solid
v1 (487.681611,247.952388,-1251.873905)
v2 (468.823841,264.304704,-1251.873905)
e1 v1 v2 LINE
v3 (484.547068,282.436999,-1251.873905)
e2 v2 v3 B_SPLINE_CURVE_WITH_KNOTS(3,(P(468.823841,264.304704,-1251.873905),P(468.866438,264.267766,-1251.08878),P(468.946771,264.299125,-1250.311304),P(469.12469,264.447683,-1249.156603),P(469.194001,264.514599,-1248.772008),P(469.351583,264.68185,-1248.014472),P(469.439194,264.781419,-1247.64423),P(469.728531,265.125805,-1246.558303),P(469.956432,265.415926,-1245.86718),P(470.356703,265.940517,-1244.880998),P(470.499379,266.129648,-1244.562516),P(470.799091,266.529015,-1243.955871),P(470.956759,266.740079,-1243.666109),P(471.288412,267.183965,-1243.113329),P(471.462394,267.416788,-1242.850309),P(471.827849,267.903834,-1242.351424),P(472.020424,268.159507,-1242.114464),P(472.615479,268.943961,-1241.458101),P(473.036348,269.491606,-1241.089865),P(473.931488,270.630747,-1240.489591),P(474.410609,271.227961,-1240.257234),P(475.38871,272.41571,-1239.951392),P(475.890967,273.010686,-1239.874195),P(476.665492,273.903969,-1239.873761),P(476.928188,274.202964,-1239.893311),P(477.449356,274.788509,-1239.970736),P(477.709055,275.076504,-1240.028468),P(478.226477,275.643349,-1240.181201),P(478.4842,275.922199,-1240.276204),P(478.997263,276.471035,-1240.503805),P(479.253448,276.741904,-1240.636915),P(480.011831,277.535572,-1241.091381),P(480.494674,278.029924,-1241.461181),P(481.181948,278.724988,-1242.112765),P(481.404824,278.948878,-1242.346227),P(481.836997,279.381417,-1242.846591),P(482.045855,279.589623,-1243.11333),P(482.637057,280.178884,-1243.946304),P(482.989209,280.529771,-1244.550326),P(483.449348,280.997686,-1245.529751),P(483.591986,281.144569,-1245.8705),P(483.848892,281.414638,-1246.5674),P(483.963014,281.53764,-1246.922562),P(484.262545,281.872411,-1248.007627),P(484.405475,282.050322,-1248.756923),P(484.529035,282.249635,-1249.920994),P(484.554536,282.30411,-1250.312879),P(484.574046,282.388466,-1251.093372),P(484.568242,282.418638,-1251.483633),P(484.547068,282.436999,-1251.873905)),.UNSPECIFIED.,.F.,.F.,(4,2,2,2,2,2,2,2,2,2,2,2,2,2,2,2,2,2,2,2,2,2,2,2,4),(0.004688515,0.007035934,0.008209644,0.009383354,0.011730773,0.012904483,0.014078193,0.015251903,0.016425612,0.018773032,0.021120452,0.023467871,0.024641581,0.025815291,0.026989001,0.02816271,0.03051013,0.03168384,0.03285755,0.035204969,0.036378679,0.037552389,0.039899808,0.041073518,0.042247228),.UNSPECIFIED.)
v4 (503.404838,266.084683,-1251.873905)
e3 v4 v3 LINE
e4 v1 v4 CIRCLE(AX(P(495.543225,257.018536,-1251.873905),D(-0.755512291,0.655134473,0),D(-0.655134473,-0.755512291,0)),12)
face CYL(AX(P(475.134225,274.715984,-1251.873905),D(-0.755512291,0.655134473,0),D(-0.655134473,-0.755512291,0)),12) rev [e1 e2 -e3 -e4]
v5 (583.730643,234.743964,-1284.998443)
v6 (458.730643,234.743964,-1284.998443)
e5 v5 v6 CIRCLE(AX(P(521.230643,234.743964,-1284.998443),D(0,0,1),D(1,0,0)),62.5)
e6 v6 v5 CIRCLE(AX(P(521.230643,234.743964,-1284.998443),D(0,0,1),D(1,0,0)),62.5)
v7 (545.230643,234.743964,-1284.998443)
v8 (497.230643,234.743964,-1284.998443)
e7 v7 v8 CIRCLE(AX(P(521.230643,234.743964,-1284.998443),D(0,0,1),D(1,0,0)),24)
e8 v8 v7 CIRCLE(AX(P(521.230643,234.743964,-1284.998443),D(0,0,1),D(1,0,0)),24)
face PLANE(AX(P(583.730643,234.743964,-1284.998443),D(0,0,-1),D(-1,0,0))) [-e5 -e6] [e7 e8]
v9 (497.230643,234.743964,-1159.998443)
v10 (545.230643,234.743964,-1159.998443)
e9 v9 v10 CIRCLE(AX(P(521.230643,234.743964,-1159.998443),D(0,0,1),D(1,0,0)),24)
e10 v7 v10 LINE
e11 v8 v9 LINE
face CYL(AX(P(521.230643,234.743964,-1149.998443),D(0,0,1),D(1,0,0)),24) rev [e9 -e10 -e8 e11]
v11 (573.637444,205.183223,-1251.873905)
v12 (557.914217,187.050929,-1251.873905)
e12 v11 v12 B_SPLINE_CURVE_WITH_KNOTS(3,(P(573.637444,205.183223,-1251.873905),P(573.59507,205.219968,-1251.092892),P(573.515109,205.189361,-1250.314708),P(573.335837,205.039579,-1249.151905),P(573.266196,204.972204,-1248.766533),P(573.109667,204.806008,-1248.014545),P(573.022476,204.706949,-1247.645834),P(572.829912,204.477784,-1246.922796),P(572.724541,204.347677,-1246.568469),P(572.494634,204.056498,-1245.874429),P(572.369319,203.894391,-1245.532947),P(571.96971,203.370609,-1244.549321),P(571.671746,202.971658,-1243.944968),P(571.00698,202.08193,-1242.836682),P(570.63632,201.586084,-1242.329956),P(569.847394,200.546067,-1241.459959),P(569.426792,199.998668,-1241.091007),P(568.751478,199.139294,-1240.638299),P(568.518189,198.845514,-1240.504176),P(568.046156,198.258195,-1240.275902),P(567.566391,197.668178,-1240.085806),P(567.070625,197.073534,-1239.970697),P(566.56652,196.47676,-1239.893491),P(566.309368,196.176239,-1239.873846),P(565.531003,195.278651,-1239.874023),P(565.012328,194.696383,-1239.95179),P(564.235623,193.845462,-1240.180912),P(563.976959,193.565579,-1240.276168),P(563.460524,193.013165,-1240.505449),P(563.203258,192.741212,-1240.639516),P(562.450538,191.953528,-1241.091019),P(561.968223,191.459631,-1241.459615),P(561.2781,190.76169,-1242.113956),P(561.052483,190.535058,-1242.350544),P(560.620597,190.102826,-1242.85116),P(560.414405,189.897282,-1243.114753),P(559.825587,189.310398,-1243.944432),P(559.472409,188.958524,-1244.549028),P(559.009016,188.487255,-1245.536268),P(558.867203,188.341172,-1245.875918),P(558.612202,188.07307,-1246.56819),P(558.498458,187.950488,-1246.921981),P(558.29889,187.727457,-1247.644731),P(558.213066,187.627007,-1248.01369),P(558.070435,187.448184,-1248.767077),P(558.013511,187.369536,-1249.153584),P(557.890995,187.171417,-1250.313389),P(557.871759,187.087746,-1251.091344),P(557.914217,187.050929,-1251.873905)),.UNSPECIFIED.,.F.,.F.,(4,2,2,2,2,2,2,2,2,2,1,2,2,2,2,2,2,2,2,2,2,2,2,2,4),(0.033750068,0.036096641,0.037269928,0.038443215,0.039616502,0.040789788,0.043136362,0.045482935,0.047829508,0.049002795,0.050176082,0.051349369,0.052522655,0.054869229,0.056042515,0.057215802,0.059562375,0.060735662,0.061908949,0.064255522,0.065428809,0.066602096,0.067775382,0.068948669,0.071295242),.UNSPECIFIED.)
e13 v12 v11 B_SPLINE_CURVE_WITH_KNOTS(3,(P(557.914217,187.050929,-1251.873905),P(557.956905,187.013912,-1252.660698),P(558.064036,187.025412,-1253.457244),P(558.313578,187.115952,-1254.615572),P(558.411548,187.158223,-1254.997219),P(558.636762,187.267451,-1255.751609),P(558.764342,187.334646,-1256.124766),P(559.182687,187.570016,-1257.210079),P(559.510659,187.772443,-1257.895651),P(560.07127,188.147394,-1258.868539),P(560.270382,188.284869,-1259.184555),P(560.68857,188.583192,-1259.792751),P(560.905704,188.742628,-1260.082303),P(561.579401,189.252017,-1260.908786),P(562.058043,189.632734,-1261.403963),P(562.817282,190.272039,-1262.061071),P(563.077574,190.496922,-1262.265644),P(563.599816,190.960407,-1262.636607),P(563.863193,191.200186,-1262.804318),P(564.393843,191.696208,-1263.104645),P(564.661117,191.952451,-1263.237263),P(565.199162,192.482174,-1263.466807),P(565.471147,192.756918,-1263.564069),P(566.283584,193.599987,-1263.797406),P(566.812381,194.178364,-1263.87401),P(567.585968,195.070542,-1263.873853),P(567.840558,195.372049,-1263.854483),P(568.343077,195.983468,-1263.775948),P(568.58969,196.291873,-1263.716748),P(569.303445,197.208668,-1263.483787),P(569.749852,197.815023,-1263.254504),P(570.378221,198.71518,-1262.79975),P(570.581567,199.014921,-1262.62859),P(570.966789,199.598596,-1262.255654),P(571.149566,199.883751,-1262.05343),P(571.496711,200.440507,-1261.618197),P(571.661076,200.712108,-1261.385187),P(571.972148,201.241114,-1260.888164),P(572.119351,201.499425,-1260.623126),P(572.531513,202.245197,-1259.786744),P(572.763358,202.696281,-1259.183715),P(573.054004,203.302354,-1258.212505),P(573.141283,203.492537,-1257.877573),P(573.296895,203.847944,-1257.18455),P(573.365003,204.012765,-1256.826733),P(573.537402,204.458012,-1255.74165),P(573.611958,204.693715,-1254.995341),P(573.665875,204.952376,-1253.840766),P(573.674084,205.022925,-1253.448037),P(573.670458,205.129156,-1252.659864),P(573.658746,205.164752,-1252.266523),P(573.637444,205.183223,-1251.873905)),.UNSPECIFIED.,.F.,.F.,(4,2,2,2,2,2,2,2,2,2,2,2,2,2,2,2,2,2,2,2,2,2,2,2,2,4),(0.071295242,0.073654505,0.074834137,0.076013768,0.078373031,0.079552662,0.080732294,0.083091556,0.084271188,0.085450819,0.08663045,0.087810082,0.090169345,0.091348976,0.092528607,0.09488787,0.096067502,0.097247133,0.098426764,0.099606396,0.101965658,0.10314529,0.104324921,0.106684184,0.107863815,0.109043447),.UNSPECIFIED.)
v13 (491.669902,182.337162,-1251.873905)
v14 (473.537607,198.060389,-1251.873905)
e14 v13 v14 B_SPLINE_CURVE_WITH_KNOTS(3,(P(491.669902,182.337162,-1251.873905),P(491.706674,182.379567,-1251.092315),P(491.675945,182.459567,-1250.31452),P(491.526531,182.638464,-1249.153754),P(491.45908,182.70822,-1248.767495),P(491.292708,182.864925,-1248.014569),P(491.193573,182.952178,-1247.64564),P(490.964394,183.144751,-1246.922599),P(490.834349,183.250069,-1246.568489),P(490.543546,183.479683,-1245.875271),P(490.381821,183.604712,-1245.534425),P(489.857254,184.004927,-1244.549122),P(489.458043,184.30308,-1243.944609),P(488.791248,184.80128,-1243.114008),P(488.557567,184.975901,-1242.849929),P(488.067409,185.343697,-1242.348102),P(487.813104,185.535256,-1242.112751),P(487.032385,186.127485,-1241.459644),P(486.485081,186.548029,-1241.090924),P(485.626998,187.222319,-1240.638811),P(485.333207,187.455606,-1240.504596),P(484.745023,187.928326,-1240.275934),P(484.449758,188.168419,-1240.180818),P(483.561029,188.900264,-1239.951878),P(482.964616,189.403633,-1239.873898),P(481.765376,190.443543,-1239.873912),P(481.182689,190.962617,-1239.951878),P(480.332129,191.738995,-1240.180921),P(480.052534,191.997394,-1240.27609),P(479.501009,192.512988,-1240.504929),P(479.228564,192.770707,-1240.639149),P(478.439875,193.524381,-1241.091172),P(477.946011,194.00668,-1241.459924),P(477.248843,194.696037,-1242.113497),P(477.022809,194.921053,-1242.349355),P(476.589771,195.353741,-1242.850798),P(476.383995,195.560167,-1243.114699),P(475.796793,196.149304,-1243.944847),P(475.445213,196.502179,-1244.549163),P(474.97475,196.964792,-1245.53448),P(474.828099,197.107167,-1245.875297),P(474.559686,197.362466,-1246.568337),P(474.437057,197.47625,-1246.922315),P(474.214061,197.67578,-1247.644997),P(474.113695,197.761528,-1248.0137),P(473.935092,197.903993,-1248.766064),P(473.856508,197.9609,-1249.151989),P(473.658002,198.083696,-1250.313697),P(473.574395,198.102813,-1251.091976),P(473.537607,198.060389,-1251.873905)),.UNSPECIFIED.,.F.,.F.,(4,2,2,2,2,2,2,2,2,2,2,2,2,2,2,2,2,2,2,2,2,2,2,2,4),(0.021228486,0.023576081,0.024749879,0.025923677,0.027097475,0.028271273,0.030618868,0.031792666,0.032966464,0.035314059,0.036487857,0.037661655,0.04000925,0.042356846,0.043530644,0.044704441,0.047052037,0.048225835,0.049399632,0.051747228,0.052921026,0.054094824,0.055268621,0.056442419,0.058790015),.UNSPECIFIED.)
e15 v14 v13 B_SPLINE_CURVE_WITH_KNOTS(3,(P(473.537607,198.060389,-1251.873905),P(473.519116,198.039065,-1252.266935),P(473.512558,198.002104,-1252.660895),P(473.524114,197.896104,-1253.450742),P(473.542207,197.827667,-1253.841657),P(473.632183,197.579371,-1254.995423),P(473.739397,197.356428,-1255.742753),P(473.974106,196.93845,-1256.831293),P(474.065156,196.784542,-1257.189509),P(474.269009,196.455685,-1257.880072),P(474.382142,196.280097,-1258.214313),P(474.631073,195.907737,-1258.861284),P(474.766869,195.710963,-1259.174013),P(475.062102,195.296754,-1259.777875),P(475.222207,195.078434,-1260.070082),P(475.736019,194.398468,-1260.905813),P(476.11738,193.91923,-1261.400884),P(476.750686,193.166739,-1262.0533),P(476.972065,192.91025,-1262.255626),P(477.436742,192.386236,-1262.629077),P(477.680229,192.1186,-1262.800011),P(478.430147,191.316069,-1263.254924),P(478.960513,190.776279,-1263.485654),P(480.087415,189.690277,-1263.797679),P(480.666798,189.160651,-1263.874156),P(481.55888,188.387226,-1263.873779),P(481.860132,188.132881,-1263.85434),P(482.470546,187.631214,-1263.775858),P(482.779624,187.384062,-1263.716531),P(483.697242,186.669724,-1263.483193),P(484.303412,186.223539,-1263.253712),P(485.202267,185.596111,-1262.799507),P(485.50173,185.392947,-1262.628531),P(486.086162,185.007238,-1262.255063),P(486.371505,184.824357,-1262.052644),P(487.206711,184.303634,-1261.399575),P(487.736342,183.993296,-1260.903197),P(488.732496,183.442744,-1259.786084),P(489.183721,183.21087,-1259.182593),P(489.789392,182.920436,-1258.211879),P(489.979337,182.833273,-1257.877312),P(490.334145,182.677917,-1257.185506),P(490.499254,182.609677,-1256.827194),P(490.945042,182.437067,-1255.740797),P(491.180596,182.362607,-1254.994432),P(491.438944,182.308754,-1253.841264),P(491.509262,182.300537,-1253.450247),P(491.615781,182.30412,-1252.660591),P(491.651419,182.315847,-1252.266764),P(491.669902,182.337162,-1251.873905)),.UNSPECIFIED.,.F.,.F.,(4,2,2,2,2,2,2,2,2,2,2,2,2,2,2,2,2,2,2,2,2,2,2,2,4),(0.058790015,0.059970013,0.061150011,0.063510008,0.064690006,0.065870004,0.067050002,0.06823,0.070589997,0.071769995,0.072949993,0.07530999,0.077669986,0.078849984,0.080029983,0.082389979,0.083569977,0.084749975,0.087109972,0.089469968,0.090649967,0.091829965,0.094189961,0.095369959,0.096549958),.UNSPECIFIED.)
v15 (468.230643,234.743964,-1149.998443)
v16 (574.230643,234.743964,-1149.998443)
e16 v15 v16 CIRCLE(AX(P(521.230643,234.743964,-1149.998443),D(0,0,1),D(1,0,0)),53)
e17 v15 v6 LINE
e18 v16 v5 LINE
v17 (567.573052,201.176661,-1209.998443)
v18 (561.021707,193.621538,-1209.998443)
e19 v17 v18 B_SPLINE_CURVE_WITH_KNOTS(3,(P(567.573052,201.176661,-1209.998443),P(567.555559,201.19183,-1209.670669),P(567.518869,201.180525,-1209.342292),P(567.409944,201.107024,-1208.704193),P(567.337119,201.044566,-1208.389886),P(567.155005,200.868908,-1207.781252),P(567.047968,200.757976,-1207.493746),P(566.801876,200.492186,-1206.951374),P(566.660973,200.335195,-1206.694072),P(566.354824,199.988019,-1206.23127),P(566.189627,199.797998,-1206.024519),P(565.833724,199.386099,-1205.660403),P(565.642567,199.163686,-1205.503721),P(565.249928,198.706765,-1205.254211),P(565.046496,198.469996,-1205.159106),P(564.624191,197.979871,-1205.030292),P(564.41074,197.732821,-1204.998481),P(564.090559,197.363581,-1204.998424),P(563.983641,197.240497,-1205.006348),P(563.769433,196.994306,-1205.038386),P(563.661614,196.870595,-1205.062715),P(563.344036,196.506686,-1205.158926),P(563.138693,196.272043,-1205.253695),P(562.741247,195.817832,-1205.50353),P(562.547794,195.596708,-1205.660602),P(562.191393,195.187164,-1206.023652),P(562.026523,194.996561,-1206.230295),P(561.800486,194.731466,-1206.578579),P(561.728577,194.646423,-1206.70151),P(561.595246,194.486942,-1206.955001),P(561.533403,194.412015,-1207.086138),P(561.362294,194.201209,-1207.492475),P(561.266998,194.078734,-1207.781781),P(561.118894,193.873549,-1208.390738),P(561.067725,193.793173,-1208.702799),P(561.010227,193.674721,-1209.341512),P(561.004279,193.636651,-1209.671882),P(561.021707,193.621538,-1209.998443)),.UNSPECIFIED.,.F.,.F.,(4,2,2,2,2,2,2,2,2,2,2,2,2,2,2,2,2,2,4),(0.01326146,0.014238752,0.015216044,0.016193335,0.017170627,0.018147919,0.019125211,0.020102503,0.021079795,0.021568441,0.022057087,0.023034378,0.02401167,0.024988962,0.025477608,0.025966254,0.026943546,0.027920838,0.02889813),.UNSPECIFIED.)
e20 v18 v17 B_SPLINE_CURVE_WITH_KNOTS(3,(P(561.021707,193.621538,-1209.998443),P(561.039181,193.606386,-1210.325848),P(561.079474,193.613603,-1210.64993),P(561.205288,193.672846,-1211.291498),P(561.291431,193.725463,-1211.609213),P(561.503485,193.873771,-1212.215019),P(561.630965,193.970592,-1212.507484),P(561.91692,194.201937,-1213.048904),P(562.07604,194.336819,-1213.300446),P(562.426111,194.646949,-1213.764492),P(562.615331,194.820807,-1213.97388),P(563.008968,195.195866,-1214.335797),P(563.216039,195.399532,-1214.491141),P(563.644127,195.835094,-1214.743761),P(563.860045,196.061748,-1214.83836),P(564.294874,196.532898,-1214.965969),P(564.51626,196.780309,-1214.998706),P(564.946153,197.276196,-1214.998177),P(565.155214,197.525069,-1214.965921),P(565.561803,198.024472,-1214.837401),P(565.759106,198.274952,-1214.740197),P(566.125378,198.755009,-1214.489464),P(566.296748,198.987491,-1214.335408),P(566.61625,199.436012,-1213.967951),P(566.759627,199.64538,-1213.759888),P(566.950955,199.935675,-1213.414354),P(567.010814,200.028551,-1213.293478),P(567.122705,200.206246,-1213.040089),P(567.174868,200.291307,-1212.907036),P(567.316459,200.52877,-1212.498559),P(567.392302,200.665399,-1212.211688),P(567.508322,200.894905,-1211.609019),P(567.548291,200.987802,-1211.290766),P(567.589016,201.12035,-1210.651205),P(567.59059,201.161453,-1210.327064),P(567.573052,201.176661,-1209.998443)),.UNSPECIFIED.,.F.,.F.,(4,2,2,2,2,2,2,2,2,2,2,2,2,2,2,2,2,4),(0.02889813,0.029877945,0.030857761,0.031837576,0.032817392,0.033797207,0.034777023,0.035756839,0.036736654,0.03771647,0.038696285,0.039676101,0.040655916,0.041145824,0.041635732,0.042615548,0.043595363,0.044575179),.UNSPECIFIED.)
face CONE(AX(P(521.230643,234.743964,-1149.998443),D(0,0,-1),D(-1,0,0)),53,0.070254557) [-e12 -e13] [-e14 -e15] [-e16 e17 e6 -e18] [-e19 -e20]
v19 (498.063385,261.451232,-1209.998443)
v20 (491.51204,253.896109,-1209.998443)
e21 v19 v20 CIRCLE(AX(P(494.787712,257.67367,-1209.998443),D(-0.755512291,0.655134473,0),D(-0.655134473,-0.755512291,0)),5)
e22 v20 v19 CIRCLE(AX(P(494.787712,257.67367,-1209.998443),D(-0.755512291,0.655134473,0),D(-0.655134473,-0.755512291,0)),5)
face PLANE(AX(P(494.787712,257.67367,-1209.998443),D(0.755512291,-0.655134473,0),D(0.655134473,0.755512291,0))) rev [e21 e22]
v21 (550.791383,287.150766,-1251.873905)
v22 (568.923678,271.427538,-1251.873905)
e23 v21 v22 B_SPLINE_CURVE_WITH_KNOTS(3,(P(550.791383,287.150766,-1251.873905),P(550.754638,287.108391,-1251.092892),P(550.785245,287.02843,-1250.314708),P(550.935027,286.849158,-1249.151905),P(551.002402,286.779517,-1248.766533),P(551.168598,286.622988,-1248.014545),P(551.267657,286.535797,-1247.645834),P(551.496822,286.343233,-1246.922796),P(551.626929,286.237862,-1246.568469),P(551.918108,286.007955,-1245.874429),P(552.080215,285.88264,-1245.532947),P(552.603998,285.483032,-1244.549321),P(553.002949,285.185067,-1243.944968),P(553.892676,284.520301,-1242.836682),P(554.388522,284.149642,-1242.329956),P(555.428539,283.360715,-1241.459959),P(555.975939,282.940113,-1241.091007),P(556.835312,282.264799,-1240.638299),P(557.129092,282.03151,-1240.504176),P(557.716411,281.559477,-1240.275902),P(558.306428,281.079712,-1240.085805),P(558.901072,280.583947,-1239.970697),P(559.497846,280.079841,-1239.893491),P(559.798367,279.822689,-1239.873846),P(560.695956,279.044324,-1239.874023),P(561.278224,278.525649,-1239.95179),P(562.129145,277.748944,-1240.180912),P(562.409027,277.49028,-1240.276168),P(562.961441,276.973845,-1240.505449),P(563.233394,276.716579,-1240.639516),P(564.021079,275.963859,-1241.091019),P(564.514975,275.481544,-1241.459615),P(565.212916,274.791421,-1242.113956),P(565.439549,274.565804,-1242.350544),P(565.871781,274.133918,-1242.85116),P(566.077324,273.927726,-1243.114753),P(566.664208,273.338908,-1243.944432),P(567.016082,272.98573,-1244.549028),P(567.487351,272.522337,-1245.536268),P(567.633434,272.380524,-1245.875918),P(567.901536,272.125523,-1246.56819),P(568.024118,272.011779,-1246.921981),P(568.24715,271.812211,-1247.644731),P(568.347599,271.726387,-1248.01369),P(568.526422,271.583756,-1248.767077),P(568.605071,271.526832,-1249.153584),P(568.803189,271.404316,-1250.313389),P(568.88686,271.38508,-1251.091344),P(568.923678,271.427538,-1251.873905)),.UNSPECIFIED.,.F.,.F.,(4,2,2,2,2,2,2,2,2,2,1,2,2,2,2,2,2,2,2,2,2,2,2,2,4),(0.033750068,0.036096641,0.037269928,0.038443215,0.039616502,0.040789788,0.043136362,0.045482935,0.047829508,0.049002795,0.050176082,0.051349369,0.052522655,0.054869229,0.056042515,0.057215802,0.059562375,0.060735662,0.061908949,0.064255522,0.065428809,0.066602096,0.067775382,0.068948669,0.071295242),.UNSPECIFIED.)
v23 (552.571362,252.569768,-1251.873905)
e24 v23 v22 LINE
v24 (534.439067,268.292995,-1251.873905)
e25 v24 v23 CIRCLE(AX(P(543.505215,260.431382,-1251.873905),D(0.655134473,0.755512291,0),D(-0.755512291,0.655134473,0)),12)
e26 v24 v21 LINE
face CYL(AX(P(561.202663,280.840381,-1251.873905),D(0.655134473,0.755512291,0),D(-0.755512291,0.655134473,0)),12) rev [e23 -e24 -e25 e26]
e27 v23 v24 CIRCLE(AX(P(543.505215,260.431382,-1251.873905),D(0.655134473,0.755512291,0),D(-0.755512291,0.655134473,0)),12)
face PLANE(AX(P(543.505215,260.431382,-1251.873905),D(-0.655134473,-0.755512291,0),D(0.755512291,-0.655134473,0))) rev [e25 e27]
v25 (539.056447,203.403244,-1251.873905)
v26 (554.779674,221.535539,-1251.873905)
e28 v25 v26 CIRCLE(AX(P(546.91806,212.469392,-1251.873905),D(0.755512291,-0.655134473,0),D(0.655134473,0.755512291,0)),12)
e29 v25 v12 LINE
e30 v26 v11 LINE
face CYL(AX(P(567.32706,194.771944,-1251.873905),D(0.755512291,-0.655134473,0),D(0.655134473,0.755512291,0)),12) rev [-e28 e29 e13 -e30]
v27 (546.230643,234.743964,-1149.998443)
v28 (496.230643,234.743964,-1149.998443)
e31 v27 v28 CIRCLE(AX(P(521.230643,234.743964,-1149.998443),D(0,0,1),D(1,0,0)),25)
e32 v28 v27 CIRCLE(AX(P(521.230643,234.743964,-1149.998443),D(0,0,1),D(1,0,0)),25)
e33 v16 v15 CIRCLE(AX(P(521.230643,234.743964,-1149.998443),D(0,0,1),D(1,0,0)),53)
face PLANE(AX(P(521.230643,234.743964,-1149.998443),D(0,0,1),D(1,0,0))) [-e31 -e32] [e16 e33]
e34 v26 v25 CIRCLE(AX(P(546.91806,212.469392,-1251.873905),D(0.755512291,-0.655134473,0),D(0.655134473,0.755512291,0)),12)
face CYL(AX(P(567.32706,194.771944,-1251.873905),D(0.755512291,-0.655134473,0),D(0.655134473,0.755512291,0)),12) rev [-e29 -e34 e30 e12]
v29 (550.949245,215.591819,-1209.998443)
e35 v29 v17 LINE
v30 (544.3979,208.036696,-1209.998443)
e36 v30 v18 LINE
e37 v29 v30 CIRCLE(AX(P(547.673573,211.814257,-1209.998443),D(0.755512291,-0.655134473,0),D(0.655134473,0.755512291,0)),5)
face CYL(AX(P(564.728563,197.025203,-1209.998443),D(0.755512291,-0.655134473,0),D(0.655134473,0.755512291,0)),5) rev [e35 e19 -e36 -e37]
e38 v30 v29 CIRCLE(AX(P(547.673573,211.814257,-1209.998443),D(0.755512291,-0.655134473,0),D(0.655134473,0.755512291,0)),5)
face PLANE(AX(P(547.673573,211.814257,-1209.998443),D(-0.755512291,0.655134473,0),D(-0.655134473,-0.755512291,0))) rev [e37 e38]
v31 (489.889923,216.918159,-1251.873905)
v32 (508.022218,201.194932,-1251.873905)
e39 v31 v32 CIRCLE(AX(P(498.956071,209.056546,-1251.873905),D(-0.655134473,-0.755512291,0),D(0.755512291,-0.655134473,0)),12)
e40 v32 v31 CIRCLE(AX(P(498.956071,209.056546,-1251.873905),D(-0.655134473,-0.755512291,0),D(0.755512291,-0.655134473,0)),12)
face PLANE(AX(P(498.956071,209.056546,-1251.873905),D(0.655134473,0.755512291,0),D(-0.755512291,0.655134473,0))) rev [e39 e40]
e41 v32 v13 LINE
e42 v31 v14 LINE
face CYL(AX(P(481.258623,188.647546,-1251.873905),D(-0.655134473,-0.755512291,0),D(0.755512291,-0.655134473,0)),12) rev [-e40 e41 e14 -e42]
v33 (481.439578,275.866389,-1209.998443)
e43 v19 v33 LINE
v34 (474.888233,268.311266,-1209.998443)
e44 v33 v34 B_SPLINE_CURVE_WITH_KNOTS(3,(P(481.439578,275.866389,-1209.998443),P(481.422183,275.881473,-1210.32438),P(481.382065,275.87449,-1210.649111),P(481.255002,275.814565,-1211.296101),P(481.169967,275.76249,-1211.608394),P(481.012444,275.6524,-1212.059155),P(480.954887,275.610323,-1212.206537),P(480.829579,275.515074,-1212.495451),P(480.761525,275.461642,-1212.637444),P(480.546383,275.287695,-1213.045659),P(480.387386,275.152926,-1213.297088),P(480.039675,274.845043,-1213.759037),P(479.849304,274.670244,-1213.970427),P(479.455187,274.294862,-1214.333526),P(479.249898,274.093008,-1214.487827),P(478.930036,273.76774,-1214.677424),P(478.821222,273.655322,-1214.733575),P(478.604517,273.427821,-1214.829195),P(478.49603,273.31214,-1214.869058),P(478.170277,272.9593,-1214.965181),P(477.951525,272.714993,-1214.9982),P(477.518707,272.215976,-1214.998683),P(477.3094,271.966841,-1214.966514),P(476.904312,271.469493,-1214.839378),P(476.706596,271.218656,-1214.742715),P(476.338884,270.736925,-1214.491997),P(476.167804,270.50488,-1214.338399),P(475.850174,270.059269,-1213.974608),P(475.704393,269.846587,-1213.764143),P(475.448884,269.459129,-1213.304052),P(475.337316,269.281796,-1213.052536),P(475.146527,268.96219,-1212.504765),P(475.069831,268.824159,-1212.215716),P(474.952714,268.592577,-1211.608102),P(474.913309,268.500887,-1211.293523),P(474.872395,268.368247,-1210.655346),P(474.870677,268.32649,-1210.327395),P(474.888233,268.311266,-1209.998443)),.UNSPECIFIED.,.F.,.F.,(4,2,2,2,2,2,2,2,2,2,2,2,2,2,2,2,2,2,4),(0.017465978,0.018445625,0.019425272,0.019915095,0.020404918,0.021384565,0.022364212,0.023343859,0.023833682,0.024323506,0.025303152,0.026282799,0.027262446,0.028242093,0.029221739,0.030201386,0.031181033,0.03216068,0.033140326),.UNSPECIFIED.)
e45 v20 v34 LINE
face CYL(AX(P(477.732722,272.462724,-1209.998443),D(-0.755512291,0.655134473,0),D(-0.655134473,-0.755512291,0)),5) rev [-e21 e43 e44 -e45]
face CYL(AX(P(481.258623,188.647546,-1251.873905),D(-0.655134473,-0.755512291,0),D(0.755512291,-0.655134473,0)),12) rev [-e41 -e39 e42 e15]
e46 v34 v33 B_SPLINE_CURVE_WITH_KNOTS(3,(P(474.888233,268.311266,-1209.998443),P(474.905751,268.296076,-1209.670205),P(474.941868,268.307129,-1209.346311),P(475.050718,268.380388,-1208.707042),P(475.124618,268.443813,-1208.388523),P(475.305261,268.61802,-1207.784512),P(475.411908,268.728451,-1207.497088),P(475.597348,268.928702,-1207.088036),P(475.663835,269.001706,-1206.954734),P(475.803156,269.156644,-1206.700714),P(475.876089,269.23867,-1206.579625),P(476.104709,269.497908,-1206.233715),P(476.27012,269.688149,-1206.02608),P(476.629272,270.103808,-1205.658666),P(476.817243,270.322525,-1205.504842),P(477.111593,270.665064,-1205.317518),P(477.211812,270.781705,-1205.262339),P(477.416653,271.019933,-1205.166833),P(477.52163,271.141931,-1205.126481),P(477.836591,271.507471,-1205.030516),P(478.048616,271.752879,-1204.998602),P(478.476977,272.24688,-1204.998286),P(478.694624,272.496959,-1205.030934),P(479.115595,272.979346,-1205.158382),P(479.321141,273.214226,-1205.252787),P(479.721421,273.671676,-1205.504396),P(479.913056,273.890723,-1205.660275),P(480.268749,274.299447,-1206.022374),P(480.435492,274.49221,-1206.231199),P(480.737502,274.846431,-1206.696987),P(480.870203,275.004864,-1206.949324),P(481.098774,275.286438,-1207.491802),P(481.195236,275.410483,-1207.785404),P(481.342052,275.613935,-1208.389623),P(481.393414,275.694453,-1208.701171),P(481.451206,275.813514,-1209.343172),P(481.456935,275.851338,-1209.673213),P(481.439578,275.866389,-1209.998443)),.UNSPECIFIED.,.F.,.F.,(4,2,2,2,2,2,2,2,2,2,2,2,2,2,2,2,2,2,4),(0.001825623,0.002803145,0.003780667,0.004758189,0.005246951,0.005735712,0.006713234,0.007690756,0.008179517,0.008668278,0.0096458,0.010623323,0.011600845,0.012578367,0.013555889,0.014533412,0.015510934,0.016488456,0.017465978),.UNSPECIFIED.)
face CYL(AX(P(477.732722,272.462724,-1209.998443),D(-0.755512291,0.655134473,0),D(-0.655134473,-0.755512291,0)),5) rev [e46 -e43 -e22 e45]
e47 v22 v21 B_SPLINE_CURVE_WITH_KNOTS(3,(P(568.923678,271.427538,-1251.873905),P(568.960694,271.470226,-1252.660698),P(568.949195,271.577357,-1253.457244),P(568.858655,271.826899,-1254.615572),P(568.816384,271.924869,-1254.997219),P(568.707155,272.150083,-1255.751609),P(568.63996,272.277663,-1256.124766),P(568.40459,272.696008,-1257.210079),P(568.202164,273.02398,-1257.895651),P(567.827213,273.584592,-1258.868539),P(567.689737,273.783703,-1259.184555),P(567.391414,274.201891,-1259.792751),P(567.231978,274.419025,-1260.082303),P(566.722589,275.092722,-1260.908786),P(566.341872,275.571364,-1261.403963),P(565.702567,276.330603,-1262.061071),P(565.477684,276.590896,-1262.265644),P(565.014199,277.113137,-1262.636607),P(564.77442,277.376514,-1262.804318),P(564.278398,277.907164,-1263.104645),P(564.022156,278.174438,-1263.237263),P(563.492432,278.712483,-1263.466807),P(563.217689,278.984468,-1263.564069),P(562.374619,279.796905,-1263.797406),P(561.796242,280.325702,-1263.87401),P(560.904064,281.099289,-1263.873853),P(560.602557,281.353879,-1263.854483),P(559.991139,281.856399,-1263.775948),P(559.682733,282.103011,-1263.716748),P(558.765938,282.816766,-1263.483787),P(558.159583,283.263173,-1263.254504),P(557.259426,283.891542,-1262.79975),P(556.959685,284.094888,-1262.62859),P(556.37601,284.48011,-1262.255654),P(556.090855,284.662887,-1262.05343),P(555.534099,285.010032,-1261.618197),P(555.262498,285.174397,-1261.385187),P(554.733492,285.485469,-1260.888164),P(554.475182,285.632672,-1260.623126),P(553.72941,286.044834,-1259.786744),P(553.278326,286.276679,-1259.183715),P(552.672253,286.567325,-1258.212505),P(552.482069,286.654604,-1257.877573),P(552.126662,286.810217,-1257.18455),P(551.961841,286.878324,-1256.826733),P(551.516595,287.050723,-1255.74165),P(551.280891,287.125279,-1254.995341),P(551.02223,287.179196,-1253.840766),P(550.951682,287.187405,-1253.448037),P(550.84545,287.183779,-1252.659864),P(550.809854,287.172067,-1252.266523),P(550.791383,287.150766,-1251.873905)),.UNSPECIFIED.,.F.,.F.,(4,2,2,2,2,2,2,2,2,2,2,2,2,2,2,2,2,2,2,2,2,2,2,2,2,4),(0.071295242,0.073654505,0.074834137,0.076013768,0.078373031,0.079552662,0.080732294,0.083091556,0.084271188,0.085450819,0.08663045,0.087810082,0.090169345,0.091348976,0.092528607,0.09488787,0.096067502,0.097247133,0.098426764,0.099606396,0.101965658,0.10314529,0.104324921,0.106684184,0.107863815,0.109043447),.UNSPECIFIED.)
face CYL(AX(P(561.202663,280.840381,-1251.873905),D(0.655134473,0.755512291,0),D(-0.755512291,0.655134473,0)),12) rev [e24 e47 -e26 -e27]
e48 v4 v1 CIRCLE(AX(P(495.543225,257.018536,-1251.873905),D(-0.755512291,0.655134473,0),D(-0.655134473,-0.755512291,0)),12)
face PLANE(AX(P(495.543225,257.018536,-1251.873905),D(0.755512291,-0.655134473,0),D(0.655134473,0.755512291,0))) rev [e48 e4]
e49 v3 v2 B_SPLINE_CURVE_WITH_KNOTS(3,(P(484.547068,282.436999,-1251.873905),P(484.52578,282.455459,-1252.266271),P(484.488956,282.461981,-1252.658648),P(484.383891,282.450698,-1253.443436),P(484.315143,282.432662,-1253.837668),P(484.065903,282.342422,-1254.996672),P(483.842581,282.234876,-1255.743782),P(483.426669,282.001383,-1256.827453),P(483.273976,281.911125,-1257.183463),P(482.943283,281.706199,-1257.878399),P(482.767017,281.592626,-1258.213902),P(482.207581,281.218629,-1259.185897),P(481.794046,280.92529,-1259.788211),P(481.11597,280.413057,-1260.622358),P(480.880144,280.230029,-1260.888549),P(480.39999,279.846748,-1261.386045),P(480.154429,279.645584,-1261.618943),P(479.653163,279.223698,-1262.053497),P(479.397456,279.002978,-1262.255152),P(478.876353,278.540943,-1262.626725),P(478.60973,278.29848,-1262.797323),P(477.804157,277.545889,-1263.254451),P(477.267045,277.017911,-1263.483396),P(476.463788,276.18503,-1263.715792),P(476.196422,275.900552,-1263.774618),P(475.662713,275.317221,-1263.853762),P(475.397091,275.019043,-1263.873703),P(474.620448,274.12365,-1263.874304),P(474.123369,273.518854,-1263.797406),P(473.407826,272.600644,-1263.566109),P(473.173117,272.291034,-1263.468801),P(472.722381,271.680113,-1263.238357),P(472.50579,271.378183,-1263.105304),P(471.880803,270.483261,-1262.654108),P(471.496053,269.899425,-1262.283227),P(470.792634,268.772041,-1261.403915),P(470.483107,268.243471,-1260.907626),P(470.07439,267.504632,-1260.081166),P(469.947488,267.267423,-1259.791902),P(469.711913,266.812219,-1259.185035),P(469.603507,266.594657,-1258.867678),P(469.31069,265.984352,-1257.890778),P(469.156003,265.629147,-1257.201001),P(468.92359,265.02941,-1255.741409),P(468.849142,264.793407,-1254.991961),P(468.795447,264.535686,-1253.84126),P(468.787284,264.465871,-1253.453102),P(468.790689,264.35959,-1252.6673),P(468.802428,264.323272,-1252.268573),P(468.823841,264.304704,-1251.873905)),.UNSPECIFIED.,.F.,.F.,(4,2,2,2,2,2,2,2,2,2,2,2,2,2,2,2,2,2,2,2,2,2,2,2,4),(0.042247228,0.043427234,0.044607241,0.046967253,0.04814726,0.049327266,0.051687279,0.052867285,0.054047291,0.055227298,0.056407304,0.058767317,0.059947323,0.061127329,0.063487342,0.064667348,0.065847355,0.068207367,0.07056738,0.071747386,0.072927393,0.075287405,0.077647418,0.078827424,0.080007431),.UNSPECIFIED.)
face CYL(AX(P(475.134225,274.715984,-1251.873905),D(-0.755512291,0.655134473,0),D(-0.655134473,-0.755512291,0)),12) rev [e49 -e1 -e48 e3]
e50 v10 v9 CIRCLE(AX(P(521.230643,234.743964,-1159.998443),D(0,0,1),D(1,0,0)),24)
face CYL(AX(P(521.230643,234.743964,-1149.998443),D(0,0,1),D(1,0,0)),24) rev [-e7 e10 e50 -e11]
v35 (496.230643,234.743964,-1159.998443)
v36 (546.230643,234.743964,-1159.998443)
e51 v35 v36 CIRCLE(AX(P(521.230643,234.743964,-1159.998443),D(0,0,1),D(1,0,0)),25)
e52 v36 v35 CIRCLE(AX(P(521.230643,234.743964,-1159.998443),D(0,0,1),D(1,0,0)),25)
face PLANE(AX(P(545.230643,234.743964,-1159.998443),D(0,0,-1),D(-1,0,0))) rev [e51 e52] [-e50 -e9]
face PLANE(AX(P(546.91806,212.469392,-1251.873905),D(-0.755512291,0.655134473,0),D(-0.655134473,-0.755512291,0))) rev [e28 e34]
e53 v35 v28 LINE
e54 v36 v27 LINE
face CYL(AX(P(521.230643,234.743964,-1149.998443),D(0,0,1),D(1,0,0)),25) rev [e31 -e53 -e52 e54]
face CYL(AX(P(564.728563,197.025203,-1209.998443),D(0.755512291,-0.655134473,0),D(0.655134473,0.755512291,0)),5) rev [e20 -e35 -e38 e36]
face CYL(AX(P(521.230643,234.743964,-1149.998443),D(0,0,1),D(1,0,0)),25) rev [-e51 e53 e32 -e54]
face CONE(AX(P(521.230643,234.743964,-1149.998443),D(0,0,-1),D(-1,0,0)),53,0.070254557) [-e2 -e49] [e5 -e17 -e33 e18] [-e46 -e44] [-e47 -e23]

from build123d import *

# Parameters (mm, degrees)
F_10_0_10_DIAMETER_HOLE1_D        = 10
F_10_0_10_DIAMETER_HOLE1_DEPTH    = 22.574074074
F_10_0_10_DIAMETER_HOLE2_D        = 10
F_10_0_10_DIAMETER_HOLE2_DEPTH    = 22.574074074
F_24_0_24_DIAMETER_HOLE1_D        = 24
F_24_0_24_DIAMETER_HOLE1_DEPTH    = 27.01345843
F_24_0_24_DIAMETER_HOLE2_D        = 24
F_24_0_24_DIAMETER_HOLE2_DEPTH    = 27.01345843
F_24_0_24_DIAMETER_HOLE3_D        = 24
F_24_0_24_DIAMETER_HOLE3_DEPTH    = 27.01345843
F_24_0_24_DIAMETER_HOLE4_D        = 24
F_24_0_24_DIAMETER_HOLE4_DEPTH    = 27.01345843
M42_COUNTERBORE_HOLE1_D           = 48
M42_COUNTERBORE_HOLE1_CBORE_D     = 50
M42_COUNTERBORE_HOLE1_CBORE_DEPTH = 10


with BuildPart() as part:
    # Sketch1 → Revolve1 (revolve)
    with BuildSketch(Plane(origin=(0, 234.743963655, 0), x_dir=(1, 0, 0), z_dir=(0, 1, 0))):
        Polygon((583.730642584, 1284.998443067), (521.230642584, 1284.998443067), (521.230642584, 1149.998443067), (574.230642584, 1149.998443067), align=None)
    revolve(axis=Axis((521.230642584, 234.743963655, -1284.998443067), (0, 0, 1)))

    # Ø10.0 (10) diameter hole1
    with Locations(Plane(origin=(137.830540227, -119.518291539, 0), x_dir=(0, 0, 1), z_dir=(-0.7555122914421019, 0.6551344728221105, -4.1215083496546135e-15))):
        with Locations((-1209.998443067, 518.828112131)):
            Hole(F_10_0_10_DIAMETER_HOLE1_D / 2, depth=F_10_0_10_DIAMETER_HOLE1_DEPTH)

    # Ø10.0 (10) diameter hole2
    with Locations(Plane(origin=(224.826381489, -194.955812873, 0), x_dir=(0, 0, -1), z_dir=(0.7555122914421021, -0.6551344728221103, 4.1124165324552015e-15))):
        with Locations((1209.998443067, 518.828112131)):
            Hole(F_10_0_10_DIAMETER_HOLE2_D / 2, depth=F_10_0_10_DIAMETER_HOLE2_DEPTH)

    # Ø24.0 (24) diameter hole1
    with Locations(Plane(origin=(135.232043071, -117.265032283, 0), x_dir=(0, 0, 1), z_dir=(-0.7555122914421021, 0.6551344728221103, 2.8630302475456504e-15))):
        with Locations((-1251.873904967, 518.828112131)):
            Hole(F_24_0_24_DIAMETER_HOLE1_D / 2, depth=F_24_0_24_DIAMETER_HOLE1_DEPTH)

    # Ø24.0 (24) diameter hole2
    with Locations(Plane(origin=(299.930161803, 345.884598073, 0), x_dir=(-0.7555122914421089, 0.6551344728221025, -3.5502706463705578e-15), z_dir=(-0.6551344728221025, -0.755512291442109, 4.094232898056383e-15))):
        with Locations((-240.007294272, 1251.873904967)):
            Hole(F_24_0_24_DIAMETER_HOLE2_D / 2, depth=F_24_0_24_DIAMETER_HOLE2_DEPTH)

    # Ø24.0 (24) diameter hole3
    with Locations(Plane(origin=(379.87420165, 438.077433648, 0), x_dir=(0.7555122914421041, -0.6551344728221079, -2.4905301953140895e-15), z_dir=(0.6551344728221079, 0.7555122914421041, 2.87212206474506e-15))):
        with Locations((240.007294272, 1251.873904967)):
            Hole(F_24_0_24_DIAMETER_HOLE3_D / 2, depth=F_24_0_24_DIAMETER_HOLE3_DEPTH)

    # Ø24.0 (24) diameter hole4
    with Locations(Plane(origin=(227.424878645, -197.20907213, 0), x_dir=(0, 0, -1), z_dir=(0.7555122914421021, -0.6551344728221103, 4.1124165324552015e-15))):
        with Locations((1251.873904967, 518.828112131)):
            Hole(F_24_0_24_DIAMETER_HOLE4_D / 2, depth=F_24_0_24_DIAMETER_HOLE4_DEPTH)

    # M42 counterbore hole1 (through all)
    with Locations(Plane.XY.offset(-1149.998443067)):
        with Locations((521.230642584, 234.743963655)):
            CounterBoreHole(M42_COUNTERBORE_HOLE1_D / 2, M42_COUNTERBORE_HOLE1_CBORE_D / 2, M42_COUNTERBORE_HOLE1_CBORE_DEPTH)


solid = part.part
